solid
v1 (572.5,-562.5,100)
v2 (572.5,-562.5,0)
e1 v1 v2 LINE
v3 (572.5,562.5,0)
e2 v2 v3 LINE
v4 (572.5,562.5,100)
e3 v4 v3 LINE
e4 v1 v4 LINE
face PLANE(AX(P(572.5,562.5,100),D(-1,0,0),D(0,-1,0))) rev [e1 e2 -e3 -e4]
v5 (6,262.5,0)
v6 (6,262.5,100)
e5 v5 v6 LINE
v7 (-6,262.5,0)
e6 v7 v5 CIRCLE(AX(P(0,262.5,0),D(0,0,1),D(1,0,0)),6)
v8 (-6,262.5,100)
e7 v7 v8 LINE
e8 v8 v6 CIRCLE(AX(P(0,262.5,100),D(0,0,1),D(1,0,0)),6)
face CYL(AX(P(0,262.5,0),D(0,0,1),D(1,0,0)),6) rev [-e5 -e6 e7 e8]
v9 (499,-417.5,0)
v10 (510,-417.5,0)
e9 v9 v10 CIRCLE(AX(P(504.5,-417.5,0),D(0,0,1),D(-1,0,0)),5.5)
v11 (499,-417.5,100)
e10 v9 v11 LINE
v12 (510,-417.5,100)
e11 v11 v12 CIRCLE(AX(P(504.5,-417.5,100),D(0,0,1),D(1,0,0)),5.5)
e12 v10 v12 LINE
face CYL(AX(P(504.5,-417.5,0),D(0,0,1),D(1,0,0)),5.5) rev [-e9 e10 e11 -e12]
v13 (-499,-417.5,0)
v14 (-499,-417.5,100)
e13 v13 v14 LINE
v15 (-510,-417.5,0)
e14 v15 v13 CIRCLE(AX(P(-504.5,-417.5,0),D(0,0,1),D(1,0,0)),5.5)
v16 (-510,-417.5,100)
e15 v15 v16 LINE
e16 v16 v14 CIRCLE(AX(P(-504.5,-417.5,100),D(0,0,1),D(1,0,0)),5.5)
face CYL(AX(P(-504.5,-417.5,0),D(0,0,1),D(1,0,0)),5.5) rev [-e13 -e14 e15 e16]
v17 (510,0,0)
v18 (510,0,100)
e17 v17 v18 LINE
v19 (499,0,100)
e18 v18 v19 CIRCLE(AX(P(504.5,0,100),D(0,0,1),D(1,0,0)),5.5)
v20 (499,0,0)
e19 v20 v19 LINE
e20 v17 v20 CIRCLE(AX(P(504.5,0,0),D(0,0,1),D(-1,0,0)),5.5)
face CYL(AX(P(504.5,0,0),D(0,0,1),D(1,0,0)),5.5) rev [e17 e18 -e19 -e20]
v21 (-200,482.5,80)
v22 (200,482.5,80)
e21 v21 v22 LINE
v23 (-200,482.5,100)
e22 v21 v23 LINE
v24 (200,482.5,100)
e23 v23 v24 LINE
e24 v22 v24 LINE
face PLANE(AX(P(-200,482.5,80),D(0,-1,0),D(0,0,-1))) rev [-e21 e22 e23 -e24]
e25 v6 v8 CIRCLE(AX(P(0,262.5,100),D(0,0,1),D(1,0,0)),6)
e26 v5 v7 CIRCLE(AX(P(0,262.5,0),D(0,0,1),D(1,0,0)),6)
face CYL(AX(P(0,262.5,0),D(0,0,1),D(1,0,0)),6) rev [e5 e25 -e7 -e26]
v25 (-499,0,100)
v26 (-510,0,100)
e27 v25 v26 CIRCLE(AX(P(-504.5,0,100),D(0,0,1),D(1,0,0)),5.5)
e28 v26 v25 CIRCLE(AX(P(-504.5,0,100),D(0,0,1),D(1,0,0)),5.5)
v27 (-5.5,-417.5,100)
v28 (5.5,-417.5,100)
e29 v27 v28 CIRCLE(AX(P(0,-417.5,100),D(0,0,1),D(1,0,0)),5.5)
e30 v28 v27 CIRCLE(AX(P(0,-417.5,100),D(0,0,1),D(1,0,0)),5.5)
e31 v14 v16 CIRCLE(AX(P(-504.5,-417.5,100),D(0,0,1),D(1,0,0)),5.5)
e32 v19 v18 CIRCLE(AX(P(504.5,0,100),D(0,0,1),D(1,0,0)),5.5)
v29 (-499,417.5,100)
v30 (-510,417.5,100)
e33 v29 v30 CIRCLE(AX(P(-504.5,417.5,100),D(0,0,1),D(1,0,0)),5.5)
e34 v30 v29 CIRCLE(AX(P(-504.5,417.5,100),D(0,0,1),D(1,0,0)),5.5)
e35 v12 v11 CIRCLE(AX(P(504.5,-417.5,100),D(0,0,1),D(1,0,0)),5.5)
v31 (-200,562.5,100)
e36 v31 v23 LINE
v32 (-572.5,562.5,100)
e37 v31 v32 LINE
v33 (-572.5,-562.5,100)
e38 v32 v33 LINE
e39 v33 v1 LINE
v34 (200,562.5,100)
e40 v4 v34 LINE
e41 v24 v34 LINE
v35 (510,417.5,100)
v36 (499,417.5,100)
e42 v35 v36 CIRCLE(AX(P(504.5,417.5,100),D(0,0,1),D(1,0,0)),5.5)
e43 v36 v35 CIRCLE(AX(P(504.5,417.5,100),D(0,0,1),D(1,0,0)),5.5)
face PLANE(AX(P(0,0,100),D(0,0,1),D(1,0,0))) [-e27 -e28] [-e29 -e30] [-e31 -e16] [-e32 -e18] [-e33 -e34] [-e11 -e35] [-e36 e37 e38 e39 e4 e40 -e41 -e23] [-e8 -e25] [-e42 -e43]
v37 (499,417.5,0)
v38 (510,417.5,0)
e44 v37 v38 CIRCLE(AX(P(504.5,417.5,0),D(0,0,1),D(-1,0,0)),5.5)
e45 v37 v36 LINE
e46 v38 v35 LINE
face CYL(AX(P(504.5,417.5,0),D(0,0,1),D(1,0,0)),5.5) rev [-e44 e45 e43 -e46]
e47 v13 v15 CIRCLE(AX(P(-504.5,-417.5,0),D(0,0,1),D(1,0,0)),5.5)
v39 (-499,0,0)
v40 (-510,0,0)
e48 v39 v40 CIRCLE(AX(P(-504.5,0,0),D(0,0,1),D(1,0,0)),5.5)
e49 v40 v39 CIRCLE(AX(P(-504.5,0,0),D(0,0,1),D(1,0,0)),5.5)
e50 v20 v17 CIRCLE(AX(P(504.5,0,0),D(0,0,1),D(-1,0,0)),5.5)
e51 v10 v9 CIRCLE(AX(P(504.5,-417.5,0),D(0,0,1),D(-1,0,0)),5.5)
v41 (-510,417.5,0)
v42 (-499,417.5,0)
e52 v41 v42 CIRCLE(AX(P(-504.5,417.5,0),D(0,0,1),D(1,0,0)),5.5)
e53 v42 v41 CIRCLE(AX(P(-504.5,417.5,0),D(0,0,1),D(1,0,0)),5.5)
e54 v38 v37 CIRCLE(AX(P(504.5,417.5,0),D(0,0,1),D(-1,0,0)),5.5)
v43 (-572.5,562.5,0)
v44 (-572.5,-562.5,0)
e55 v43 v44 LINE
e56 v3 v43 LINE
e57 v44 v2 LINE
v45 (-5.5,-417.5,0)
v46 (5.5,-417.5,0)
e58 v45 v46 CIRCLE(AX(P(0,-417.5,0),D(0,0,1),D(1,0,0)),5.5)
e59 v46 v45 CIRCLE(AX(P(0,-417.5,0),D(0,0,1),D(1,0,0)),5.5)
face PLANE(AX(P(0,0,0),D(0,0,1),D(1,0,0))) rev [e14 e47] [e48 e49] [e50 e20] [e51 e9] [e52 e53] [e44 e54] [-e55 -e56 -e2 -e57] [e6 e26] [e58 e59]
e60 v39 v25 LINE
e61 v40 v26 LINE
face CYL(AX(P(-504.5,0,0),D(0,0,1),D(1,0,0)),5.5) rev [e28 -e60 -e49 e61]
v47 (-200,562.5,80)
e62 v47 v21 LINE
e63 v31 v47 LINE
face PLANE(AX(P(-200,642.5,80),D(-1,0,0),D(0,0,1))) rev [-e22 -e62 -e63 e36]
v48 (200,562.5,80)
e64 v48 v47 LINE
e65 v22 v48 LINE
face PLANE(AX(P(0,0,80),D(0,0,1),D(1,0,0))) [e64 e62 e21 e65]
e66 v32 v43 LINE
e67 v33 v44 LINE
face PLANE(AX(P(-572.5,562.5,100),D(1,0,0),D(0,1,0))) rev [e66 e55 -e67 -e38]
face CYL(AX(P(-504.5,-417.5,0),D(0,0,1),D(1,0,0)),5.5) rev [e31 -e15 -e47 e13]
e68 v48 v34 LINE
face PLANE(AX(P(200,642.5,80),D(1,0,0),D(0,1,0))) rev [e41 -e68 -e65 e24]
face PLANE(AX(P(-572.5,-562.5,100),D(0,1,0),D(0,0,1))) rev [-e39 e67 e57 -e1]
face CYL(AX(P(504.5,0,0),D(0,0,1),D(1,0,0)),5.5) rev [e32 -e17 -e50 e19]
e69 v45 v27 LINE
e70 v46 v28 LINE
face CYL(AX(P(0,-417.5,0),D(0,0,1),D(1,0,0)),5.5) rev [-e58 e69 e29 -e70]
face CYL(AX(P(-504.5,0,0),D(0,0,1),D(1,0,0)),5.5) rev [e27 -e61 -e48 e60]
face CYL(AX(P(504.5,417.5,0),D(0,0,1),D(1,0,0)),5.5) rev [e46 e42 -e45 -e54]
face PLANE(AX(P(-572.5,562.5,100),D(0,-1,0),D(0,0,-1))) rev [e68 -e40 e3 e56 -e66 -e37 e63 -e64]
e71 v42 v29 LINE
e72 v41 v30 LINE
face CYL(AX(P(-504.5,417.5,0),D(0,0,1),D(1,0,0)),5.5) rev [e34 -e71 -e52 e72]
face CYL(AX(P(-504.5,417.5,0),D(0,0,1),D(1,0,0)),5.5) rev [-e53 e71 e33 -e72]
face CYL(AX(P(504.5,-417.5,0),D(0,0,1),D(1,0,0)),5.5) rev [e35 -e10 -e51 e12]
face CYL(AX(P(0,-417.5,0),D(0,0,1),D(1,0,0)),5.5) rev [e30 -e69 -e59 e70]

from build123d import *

# Parameters (mm, degrees)
SKETCH_1_W               = 1145
SKETCH_1_H               = 1125
EXTRUDE_1_DEPTH          = 100
SKETCH_2_W               = 400
SKETCH_2_H               = 160
CUT_EXTRUDE_1_DEPTH      = 20
CUT_EXTRUDE_2_DEPTH      = 809.803128085
CUT_EXTRUDE_2_DEPTH_BACK = 809.803128085
SKETCH_4_R               = 5.5
CUT_EXTRUDE_3_DEPTH      = 809.803128085
CUT_EXTRUDE_3_DEPTH_BACK = 809.803128085
SKETCH_3_R               = 6


with BuildPart() as part:
    # 草图1 → 凸台-拉伸1 (new body)
    with BuildSketch(Plane.XY):
        Rectangle(SKETCH_1_W, SKETCH_1_H)
    extrude(amount=EXTRUDE_1_DEPTH)

    # 草图2 → 切除-拉伸1 (cut)
    with BuildSketch(Plane.XY.offset(100)):
        with Locations((0, 562.5)):
            Rectangle(SKETCH_2_W, SKETCH_2_H)
    extrude(amount=-CUT_EXTRUDE_1_DEPTH, mode=Mode.SUBTRACT)

    # 草图4 → 切除-拉伸2 (cut, two sides: drawn at the far end of the back side and taken through both)
    with BuildSketch(Plane.XY.offset(100).offset(-CUT_EXTRUDE_2_DEPTH_BACK)):
        with Locations((-504.5, 417.5)):
            Circle(SKETCH_4_R)
        with Locations((-504.5, -417.5)):
            Circle(SKETCH_4_R)
        with Locations((504.5, -417.5)):
            Circle(SKETCH_4_R)
        with Locations((504.5, 417.5)):
            Circle(SKETCH_4_R)
        with Locations((0, -417.5)):
            Circle(SKETCH_4_R)
        with Locations((-504.5, 0)):
            Circle(SKETCH_4_R)
        with Locations((504.5, 0)):
            Circle(SKETCH_4_R)
    extrude(amount=CUT_EXTRUDE_2_DEPTH + CUT_EXTRUDE_2_DEPTH_BACK, mode=Mode.SUBTRACT)

    # 草图3 → 切除-拉伸3 (cut, two sides: drawn at the far end of the back side and taken through both)
    with BuildSketch(Plane.XY.offset(100).offset(-CUT_EXTRUDE_3_DEPTH_BACK)):
        with Locations((0, 262.5)):
            Circle(SKETCH_3_R)
    extrude(amount=CUT_EXTRUDE_3_DEPTH + CUT_EXTRUDE_3_DEPTH_BACK, mode=Mode.SUBTRACT)


solid = part.part
